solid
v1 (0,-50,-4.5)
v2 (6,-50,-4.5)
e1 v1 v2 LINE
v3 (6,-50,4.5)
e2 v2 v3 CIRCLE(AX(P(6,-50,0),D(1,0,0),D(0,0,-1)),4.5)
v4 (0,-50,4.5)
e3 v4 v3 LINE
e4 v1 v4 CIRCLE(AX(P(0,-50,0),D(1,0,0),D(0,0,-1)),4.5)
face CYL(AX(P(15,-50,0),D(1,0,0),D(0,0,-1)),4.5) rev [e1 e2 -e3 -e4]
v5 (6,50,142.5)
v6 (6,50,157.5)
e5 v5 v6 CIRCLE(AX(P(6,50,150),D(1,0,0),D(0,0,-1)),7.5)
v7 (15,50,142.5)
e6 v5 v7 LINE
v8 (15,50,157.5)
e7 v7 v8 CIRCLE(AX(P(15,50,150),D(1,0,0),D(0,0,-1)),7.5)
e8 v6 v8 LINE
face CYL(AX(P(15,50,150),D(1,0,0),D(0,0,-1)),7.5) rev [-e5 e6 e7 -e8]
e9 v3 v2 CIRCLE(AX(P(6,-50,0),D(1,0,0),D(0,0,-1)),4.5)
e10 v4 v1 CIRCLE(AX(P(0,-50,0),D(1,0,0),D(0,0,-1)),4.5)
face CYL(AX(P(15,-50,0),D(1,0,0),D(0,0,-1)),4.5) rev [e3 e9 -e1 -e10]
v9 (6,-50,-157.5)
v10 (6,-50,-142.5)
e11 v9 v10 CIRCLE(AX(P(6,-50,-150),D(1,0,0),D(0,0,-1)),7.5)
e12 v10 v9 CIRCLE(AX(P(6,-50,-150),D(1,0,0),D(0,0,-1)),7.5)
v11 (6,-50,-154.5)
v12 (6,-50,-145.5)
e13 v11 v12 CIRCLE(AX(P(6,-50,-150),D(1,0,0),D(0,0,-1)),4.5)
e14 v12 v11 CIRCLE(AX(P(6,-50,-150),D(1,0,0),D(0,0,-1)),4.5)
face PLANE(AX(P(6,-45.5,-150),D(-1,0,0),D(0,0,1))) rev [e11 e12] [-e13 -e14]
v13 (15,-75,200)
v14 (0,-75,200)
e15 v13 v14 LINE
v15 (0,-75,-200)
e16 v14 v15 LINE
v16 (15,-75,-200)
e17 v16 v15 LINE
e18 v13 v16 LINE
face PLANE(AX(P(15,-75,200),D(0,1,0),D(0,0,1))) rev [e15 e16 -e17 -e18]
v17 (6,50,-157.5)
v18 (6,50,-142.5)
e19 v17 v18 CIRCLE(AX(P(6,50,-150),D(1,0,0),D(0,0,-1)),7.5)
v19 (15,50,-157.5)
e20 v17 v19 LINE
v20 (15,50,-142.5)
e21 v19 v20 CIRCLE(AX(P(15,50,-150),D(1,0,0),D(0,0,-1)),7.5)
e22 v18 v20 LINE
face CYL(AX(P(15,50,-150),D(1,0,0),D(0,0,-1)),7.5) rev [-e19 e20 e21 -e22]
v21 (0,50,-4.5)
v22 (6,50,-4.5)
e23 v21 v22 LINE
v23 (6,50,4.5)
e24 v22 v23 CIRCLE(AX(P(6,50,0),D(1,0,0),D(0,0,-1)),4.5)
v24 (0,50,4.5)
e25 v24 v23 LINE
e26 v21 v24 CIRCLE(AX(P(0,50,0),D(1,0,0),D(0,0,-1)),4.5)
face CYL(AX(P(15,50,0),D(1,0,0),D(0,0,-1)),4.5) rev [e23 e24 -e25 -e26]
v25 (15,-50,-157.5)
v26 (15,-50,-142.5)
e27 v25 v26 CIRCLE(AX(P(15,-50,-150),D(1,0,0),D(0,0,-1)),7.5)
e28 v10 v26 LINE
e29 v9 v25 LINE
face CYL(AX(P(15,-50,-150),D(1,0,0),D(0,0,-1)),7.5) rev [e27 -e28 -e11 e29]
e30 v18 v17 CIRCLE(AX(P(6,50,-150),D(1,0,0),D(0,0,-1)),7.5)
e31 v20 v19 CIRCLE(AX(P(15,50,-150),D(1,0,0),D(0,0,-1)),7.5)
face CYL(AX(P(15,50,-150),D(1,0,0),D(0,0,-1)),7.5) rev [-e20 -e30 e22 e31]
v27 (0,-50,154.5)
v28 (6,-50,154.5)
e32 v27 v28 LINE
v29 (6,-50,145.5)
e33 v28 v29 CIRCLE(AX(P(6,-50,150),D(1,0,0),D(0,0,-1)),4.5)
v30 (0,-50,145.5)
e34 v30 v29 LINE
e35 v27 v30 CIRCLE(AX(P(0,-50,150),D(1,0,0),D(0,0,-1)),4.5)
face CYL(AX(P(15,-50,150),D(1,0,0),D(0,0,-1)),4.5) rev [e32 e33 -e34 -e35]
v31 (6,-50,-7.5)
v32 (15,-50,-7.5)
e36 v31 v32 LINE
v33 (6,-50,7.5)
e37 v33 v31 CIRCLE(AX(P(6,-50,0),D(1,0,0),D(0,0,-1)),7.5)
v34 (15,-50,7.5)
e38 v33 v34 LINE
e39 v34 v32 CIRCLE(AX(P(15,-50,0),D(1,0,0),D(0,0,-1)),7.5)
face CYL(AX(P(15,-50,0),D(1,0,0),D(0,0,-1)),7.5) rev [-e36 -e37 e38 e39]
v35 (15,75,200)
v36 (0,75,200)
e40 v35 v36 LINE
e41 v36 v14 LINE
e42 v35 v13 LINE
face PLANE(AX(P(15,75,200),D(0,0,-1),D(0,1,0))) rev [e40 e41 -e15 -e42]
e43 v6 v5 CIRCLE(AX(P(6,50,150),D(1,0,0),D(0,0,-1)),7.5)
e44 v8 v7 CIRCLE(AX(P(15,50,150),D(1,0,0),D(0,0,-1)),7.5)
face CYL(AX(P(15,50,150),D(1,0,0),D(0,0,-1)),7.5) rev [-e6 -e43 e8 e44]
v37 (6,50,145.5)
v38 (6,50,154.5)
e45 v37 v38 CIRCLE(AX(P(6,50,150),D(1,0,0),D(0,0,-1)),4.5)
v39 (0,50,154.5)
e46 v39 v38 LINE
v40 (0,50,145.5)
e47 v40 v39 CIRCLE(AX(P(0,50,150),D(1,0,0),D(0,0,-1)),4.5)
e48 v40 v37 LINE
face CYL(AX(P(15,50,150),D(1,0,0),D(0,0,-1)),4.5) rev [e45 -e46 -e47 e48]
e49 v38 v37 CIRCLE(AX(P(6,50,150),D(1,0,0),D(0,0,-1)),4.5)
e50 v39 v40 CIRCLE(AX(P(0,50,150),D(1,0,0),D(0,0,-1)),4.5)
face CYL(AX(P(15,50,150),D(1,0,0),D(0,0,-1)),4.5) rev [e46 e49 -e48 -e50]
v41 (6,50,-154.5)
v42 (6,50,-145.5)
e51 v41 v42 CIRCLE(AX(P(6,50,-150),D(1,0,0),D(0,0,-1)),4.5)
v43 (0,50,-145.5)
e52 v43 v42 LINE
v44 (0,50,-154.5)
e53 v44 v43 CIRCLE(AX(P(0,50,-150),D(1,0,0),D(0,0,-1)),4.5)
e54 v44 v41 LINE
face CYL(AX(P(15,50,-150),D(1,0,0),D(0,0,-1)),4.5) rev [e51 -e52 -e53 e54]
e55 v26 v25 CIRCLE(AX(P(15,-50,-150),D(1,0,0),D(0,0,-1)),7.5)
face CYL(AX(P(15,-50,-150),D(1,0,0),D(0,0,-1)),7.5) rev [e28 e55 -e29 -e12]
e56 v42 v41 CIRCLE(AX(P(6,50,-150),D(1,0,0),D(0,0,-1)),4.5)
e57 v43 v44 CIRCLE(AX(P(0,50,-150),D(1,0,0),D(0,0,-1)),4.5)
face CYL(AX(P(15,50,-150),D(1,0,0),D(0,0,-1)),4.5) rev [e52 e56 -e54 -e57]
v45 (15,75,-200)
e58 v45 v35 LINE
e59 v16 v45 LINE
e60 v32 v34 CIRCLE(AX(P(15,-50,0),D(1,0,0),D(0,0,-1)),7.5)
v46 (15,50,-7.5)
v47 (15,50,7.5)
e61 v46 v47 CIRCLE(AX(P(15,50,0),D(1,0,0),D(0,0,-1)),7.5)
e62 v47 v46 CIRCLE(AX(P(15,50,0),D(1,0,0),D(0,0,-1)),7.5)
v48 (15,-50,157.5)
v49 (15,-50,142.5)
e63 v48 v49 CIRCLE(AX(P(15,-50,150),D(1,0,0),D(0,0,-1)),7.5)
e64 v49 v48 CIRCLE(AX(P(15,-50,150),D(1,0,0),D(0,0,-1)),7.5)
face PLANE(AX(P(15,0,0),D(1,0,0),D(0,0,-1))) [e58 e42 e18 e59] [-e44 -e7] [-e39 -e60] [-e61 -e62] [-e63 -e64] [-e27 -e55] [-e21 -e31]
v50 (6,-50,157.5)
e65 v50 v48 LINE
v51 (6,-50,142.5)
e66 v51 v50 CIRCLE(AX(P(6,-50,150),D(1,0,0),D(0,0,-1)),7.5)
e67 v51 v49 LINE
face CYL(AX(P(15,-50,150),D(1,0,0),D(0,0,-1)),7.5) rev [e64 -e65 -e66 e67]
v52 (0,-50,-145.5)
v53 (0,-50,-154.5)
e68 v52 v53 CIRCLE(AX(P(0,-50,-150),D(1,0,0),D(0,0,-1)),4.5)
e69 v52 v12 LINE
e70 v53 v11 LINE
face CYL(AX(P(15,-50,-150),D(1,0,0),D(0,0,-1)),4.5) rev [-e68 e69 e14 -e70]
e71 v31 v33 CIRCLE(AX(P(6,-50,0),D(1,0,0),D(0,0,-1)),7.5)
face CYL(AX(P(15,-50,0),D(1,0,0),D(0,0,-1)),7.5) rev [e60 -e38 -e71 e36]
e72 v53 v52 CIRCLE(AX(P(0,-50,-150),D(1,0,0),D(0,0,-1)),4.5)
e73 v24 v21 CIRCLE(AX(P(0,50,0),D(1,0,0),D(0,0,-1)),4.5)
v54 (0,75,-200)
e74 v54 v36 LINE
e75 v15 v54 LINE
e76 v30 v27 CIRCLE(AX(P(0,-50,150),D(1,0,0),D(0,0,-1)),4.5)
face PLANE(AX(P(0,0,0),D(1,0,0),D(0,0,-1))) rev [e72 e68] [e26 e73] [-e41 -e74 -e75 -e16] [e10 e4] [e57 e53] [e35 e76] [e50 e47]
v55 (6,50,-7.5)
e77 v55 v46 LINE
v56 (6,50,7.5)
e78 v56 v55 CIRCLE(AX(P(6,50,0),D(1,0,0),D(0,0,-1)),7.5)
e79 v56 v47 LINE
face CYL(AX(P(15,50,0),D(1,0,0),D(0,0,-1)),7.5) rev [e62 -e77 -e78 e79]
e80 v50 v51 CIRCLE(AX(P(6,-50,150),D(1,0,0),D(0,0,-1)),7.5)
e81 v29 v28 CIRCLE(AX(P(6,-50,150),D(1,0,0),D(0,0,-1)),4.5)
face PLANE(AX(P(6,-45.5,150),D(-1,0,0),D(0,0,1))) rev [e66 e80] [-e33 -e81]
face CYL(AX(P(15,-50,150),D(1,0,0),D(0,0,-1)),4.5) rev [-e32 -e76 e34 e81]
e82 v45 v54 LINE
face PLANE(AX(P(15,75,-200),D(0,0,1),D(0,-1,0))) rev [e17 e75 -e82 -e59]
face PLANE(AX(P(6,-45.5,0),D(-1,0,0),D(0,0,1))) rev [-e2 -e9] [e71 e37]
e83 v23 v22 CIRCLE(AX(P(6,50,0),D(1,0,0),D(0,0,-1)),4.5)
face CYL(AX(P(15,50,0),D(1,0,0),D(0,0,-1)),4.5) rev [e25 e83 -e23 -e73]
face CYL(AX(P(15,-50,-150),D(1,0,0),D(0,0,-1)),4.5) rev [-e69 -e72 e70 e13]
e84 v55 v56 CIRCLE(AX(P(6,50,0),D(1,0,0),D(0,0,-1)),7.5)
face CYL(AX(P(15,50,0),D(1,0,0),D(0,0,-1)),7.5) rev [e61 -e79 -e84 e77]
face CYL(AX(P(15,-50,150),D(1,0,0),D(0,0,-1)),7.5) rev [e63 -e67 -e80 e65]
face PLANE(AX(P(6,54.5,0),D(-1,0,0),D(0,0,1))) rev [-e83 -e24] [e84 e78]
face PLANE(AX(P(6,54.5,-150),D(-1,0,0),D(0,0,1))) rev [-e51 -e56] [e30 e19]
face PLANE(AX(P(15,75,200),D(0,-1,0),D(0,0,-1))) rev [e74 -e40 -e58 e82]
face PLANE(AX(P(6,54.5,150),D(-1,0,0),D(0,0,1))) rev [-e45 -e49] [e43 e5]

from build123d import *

# Parameters (mm, degrees)
SKETCH_1_W                = 400
SKETCH_1_H                = 150
EXTRUDE_1_DEPTH           = 15
HOLE_WIZARD_1_D           = 9
HOLE_WIZARD_1_CBORE_D     = 15
HOLE_WIZARD_1_CBORE_DEPTH = 9


with BuildPart() as part:
    # 草图1 → 凸台-拉伸1 (new body)
    with BuildSketch(Plane(origin=(0, 0, 0), x_dir=(0, 0, -1), z_dir=(1, 0, 0))):
        Rectangle(SKETCH_1_W, SKETCH_1_H)
    extrude(amount=EXTRUDE_1_DEPTH)

    # 打孔尺寸(%根据)内六角圆柱头螺钉的类型1 (through all)
    with Locations(Plane(origin=(15, 0, 0), x_dir=(0, 0, -1), z_dir=(1, 0, 0))):
        with Locations((-150, 50), (0, 50), (150, 50), (-150, -50), (0, -50), (150, -50)):
            CounterBoreHole(HOLE_WIZARD_1_D / 2, HOLE_WIZARD_1_CBORE_D / 2, HOLE_WIZARD_1_CBORE_DEPTH)


solid = part.part
